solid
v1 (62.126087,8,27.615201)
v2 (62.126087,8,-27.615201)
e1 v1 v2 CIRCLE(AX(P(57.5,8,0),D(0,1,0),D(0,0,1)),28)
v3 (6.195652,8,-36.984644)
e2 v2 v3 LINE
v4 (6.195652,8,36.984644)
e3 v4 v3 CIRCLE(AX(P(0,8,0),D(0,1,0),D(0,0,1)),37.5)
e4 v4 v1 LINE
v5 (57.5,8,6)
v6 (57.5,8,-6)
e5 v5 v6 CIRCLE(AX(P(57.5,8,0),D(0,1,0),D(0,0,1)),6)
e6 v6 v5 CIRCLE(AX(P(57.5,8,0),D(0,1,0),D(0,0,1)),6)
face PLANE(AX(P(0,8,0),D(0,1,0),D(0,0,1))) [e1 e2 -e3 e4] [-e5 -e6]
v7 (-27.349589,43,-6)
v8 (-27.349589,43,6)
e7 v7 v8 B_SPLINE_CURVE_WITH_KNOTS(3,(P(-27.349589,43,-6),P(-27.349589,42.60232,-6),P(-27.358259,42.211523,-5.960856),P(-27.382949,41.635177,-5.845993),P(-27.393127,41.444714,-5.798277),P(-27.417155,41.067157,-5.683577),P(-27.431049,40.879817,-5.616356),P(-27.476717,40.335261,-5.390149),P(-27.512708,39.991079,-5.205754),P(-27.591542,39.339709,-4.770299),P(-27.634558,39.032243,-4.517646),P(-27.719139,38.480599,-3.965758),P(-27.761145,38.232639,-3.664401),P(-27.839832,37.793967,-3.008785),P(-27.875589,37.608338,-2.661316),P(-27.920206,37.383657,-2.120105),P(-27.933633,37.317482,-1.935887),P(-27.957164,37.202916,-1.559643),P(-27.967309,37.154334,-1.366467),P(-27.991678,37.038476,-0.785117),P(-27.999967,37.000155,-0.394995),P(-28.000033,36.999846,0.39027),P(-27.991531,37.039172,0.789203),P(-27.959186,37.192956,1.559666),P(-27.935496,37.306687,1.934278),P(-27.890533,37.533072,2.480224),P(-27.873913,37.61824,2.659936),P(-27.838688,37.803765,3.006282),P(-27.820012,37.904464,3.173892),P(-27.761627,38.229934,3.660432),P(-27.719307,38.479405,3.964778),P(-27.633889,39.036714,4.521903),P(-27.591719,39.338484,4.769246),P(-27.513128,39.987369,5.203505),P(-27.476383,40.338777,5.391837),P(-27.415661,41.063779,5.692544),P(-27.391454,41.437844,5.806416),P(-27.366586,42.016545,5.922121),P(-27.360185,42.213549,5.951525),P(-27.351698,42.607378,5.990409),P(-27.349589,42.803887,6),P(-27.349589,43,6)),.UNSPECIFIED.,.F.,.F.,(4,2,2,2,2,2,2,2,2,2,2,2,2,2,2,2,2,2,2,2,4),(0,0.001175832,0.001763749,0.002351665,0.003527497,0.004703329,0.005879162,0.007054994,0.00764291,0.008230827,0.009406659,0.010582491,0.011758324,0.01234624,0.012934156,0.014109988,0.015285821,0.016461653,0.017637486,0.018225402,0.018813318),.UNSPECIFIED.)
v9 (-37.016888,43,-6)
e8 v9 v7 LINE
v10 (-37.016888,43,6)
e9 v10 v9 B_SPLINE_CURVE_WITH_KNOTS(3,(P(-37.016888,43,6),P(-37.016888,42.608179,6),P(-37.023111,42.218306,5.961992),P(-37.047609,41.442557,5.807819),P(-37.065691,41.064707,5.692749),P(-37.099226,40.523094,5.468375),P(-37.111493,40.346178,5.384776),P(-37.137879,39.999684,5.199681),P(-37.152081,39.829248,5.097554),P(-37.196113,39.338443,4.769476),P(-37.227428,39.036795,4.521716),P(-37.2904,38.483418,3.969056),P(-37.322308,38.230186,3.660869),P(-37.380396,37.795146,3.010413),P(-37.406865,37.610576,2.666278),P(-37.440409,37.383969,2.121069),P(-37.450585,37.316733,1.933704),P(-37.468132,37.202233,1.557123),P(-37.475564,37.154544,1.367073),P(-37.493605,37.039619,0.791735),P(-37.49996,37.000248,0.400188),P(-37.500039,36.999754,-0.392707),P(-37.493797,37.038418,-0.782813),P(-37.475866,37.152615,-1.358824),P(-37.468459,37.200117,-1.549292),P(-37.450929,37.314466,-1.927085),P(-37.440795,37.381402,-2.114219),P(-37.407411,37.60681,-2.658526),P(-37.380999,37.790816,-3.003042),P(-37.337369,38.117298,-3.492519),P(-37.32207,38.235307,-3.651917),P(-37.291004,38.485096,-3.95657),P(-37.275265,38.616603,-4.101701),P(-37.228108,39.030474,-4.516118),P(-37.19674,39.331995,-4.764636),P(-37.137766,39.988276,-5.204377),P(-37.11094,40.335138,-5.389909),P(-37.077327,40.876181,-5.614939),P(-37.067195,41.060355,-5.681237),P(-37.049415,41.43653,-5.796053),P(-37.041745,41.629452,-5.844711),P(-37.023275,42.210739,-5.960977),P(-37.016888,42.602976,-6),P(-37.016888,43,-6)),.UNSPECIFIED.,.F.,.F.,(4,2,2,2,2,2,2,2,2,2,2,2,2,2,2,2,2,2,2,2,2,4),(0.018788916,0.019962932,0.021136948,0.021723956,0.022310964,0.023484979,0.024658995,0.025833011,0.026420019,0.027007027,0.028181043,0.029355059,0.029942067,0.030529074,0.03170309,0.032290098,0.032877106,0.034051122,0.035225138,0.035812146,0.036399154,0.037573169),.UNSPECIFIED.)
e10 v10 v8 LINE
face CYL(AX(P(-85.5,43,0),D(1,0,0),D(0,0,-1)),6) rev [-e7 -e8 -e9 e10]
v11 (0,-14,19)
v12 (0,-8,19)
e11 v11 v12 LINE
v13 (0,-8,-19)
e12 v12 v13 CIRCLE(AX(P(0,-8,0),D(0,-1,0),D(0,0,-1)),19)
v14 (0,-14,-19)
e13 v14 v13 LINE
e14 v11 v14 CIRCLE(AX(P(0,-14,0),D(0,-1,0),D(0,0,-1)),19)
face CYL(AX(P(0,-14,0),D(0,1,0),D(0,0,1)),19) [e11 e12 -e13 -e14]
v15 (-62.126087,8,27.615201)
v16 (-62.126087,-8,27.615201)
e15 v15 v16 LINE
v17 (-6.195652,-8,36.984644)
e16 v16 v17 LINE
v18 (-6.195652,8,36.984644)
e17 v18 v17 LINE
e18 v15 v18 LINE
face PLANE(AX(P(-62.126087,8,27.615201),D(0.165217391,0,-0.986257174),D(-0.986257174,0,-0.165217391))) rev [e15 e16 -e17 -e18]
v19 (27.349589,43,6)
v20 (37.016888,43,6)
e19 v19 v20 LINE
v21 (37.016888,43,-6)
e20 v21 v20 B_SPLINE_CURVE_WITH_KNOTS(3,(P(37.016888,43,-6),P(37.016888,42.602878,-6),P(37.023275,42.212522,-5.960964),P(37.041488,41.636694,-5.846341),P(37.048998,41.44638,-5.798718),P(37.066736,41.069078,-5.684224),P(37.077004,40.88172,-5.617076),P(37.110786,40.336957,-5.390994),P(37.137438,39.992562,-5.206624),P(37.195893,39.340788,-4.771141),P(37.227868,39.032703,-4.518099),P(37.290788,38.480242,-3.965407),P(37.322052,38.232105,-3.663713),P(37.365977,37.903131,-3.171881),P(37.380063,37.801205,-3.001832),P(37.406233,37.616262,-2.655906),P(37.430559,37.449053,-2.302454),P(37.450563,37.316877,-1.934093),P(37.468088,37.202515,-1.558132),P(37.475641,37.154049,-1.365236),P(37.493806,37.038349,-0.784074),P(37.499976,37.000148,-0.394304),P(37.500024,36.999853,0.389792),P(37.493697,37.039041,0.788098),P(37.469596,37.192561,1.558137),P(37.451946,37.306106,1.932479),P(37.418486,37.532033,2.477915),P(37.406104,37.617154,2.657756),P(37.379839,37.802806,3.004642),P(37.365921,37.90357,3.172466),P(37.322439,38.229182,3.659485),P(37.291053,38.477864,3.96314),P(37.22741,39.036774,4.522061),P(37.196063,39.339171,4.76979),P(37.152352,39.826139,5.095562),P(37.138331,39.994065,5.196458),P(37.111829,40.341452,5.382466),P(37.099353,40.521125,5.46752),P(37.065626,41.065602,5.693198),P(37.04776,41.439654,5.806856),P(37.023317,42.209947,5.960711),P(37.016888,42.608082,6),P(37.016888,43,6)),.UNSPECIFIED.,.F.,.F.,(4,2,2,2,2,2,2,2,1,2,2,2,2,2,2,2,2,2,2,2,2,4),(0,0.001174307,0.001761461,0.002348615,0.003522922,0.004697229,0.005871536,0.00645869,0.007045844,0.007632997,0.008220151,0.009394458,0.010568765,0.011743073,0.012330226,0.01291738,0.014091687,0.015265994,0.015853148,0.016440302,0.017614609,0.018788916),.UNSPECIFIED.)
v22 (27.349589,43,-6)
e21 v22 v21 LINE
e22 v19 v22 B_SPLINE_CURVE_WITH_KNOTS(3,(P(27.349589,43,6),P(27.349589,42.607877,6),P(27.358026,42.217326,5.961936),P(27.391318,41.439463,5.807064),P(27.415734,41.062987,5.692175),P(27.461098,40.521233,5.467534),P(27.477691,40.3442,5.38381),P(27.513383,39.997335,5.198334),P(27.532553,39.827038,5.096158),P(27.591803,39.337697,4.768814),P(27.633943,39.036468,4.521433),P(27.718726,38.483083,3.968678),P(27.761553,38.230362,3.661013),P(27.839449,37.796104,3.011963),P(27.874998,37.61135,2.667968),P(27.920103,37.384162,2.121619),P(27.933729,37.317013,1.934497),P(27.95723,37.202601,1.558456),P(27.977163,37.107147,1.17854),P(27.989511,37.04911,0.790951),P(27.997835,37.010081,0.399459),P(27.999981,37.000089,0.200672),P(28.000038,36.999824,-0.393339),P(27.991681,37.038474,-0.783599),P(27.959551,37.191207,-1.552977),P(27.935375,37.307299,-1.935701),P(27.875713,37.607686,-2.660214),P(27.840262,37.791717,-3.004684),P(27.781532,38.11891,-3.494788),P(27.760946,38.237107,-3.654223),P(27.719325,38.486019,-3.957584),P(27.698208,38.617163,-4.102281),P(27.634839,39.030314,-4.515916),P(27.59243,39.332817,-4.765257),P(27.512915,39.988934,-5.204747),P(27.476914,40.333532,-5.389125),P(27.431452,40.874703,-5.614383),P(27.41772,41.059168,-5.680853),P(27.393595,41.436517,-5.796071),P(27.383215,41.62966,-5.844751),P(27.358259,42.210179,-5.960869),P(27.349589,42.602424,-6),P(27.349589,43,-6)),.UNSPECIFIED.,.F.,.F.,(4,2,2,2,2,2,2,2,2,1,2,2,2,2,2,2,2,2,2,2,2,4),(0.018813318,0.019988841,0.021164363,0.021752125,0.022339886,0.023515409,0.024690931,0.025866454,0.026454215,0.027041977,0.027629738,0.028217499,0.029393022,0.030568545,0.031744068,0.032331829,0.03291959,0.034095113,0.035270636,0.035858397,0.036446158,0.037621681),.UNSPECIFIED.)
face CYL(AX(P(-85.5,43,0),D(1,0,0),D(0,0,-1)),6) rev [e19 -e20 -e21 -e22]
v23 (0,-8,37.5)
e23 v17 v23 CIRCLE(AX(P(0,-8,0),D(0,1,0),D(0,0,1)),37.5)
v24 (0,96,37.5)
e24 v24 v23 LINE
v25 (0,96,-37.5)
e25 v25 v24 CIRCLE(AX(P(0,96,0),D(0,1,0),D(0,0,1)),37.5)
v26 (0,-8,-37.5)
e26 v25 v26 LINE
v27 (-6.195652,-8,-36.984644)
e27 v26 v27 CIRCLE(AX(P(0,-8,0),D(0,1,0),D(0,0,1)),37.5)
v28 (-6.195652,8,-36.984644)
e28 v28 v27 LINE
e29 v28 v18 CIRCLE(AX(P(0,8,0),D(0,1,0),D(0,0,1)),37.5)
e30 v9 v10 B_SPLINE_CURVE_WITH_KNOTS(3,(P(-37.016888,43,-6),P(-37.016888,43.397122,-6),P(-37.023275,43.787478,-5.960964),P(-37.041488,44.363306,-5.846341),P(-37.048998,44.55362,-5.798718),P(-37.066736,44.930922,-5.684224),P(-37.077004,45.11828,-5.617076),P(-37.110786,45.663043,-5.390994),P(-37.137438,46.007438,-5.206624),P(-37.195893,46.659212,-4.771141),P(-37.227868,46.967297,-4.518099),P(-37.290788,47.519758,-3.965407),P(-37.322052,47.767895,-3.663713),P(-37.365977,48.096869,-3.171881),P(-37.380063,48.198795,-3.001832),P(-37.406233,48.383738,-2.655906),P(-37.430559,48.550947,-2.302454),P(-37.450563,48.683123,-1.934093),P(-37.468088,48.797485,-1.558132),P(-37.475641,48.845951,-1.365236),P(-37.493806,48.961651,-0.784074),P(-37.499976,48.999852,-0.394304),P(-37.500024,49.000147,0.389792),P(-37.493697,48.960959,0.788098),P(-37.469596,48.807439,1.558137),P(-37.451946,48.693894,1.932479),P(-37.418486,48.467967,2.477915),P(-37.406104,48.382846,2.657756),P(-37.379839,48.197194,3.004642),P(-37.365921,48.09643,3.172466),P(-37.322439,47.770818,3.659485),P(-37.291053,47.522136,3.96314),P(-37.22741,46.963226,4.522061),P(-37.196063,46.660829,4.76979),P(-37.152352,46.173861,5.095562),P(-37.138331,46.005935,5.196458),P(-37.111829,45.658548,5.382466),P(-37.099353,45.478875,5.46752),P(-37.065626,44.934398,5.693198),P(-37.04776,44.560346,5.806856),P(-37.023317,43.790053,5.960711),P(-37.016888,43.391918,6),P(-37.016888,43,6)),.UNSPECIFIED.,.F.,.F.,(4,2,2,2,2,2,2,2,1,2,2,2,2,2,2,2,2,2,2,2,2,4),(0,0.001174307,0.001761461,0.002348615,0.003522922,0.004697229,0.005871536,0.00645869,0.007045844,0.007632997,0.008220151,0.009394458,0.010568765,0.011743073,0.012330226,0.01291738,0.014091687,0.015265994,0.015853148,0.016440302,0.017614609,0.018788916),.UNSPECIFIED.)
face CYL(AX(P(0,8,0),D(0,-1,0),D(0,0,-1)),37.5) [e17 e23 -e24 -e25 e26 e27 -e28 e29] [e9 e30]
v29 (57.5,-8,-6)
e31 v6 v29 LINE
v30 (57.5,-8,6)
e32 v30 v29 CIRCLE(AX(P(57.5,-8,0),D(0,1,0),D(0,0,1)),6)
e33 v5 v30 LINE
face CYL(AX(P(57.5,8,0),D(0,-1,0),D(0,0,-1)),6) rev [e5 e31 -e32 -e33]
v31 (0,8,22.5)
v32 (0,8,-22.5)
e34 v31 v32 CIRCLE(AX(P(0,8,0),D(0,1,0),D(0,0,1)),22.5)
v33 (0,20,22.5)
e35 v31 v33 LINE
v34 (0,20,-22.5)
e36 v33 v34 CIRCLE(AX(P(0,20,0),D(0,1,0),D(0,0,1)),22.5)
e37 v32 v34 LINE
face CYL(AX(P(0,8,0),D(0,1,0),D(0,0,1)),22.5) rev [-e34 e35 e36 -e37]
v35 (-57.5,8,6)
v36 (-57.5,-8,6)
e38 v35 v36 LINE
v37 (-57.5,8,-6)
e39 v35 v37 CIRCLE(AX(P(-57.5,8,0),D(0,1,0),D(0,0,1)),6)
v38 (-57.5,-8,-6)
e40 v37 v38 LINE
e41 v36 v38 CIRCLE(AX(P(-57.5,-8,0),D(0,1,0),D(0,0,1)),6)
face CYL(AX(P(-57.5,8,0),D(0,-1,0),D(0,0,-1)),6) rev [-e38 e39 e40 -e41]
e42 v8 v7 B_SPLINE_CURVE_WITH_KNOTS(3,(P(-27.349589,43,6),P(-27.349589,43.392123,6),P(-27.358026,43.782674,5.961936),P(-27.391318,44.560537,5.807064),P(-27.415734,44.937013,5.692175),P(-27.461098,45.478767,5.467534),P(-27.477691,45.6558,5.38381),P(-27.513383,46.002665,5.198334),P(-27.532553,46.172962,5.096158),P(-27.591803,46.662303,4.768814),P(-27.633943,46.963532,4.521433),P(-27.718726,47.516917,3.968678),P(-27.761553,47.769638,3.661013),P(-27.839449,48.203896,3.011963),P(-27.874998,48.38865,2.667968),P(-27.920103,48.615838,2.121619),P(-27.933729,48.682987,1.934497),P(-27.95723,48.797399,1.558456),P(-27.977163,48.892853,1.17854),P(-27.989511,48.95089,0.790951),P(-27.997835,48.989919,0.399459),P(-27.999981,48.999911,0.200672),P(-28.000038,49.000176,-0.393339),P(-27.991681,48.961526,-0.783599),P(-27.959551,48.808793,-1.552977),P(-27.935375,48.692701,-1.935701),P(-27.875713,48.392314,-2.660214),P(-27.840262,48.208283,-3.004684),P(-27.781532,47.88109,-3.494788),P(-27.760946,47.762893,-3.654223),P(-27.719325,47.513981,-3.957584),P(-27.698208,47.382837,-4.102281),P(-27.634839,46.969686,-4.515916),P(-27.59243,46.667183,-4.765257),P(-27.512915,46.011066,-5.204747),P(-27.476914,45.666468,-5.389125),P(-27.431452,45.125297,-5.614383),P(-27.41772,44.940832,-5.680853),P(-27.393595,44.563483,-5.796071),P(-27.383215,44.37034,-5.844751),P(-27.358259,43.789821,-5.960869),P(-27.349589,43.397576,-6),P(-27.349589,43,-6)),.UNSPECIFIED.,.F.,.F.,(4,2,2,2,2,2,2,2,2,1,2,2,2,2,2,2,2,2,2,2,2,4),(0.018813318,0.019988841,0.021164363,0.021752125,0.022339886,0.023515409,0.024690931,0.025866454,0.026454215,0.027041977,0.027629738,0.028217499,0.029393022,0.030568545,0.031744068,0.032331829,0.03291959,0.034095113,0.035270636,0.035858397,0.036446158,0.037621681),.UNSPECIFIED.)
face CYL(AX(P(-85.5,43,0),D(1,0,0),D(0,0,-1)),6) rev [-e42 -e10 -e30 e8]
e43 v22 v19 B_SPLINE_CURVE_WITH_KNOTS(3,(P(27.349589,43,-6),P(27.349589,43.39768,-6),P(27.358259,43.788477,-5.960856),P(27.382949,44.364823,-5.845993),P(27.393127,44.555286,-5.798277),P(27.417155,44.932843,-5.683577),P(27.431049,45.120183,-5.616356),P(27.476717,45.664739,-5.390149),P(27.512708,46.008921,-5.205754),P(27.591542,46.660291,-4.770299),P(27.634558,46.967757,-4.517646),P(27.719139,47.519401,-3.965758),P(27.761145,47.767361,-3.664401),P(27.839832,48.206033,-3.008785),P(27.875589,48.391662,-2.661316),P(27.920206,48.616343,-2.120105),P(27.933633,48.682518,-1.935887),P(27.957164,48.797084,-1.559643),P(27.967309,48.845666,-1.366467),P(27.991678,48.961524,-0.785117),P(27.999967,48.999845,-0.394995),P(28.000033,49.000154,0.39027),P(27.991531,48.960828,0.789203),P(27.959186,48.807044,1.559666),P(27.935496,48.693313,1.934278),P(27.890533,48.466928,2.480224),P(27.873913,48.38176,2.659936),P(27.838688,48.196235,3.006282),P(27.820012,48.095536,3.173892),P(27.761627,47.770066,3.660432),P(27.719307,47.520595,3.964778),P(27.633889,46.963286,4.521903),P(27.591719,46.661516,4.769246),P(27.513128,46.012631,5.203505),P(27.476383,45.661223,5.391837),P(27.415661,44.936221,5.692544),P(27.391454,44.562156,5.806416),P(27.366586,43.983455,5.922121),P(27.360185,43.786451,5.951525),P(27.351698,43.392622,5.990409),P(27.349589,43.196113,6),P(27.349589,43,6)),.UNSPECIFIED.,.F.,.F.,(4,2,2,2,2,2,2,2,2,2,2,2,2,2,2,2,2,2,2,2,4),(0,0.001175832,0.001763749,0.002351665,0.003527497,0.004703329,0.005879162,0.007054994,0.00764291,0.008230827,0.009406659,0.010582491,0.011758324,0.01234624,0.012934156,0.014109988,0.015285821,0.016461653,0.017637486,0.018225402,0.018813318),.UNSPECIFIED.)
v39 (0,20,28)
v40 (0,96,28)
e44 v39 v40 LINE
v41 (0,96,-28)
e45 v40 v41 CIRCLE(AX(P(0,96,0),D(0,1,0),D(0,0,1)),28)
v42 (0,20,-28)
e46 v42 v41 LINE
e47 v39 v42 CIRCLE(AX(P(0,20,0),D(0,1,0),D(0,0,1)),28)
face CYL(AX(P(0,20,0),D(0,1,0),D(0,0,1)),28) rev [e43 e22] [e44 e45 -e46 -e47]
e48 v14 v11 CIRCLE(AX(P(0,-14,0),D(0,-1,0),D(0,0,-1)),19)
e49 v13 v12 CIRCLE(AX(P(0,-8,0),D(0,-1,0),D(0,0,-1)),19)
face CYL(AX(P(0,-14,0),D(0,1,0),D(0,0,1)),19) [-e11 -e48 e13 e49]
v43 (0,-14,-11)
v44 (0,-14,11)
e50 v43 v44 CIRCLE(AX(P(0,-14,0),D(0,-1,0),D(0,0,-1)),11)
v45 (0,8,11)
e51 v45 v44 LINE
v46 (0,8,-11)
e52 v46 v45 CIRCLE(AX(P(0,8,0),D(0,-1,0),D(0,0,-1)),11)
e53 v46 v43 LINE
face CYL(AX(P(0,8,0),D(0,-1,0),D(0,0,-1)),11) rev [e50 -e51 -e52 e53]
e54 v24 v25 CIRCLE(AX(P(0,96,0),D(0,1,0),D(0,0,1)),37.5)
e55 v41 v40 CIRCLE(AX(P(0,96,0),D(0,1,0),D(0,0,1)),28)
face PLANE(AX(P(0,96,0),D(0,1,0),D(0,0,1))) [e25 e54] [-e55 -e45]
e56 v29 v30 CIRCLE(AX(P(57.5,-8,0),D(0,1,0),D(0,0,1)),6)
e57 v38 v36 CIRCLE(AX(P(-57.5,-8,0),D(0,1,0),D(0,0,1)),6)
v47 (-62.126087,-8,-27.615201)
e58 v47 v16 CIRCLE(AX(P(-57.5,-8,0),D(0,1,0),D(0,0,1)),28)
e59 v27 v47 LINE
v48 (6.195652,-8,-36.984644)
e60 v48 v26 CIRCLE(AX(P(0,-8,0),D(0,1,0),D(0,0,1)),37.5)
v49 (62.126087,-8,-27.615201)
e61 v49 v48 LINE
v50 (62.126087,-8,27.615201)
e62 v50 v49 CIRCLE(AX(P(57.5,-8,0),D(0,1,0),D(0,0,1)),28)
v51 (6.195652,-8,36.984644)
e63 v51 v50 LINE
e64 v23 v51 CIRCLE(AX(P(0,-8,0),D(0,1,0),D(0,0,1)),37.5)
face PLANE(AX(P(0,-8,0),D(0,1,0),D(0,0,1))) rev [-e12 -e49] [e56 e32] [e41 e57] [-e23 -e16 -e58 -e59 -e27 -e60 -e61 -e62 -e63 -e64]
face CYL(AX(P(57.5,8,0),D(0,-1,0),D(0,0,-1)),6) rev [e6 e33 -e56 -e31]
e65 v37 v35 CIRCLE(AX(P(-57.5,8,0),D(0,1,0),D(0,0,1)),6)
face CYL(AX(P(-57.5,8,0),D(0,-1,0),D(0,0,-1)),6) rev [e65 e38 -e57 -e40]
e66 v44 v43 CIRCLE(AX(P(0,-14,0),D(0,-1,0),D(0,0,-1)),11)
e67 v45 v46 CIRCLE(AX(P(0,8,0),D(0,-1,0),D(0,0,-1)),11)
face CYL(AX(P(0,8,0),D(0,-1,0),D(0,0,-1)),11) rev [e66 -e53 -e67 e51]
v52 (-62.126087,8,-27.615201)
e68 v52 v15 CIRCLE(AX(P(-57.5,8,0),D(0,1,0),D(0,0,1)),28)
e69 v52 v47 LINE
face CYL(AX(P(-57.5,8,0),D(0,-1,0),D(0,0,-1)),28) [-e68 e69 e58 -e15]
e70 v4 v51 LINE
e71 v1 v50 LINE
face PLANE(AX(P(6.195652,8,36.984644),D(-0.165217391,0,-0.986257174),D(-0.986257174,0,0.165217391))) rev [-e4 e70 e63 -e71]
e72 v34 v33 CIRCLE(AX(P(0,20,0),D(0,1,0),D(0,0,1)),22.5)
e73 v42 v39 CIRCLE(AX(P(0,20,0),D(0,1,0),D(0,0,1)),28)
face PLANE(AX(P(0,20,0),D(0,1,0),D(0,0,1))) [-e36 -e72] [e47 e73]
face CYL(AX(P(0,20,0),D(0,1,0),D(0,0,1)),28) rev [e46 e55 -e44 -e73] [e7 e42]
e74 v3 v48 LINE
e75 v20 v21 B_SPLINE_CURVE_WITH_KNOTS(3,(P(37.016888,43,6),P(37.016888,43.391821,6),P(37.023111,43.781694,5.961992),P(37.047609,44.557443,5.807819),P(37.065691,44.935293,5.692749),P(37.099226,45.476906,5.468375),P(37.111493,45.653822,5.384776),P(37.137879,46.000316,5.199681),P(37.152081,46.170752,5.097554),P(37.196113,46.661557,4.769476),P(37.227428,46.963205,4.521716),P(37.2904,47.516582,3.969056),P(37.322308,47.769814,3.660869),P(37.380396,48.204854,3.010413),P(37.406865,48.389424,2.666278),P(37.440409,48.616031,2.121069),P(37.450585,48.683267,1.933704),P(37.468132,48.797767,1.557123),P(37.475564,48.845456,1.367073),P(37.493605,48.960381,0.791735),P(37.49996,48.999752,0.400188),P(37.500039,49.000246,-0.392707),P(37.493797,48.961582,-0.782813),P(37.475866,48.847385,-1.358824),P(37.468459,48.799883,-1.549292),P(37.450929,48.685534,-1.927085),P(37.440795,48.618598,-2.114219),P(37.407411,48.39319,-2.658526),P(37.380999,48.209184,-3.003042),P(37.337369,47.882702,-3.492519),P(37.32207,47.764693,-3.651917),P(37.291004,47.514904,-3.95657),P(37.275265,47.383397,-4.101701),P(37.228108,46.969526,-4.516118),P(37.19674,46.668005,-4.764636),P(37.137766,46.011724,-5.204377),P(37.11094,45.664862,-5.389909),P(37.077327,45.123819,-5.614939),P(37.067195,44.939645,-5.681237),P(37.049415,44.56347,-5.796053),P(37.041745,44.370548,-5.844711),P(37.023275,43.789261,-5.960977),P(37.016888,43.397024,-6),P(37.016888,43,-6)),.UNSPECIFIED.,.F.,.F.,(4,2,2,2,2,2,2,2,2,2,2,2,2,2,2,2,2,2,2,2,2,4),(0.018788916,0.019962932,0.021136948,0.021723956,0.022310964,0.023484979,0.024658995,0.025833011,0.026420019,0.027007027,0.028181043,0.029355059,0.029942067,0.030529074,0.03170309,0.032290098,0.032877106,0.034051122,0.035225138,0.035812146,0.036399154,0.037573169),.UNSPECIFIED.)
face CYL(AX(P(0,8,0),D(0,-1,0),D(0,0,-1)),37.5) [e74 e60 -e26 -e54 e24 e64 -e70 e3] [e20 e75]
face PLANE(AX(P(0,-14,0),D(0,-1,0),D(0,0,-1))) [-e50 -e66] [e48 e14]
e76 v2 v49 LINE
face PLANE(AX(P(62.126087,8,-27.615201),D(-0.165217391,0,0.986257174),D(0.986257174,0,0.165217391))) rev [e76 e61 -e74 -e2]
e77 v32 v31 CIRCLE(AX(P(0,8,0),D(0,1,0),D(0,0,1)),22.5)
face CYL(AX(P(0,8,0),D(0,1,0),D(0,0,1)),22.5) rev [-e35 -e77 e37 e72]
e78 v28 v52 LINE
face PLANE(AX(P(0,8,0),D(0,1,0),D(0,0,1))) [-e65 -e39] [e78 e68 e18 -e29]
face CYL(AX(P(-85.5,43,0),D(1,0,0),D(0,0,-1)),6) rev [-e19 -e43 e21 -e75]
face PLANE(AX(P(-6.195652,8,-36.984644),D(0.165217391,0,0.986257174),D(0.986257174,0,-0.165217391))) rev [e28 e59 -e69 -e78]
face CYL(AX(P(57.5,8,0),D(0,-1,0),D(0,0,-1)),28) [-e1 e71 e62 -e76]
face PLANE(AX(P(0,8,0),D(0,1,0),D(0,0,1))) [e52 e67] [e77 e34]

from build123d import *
from build123d.topology import SkipClean

# Parameters (mm, degrees)
BASE_FLANGE_SKETCH_R     = 6
BASE_FLANGE_DEPTH        = 8
TUBE_START               = 88
TUBE_SKETCH_R            = 37.5
TUBE_75_DEPTH            = 88
BORE_SKETCH_R            = 28
BORE_56_DEPTH            = 76
SPIGOT_SKETCH_R          = 19
SPIGOT_38_DEPTH          = 6
SPIGOT_HOLE_SKETCH_R     = 11
SPIGOT_HOLE_22_DEPTH     = 22
BORE_STEP_SKETCH_R       = 22.5
BORE_STEP_45_DEPTH       = 12
CROSS_HOLE_12_DEPTH      = 134.912284724
CROSS_HOLE_12_DEPTH_BACK = 134.912284724
CROSS_HOLE_SKETCH_R      = 6


with BuildPart() as part:
    # Base Flange Sketch → Base Flange (new, symmetric)
    with BuildSketch(Plane(origin=(0, 0, 0), x_dir=(1, 0, 0), z_dir=(0, 1, 0))):
        with BuildLine():
            Line((-62.126086957, -27.615200877), (-6.195652174, -36.984644032))
            ThreePointArc((-6.195652174, -36.984644032), (0, -37.5), (6.195652174, -36.984644032))
            Line((6.195652174, -36.984644032), (62.126086957, -27.615200877))
            ThreePointArc((62.126086957, -27.615200877), (85.5, 0), (62.126086957, 27.615200877))
            Line((62.126086957, 27.615200877), (6.195652174, 36.984644032))
            ThreePointArc((6.195652174, 36.984644032), (0, 37.5), (-6.195652174, 36.984644032))
            Line((-6.195652174, 36.984644032), (-62.126086957, 27.615200877))
            ThreePointArc((-62.126086957, 27.615200877), (-85.5, 0), (-62.126086957, -27.615200877))
        make_face()
        with Locations(Location((-57.5, 0, 0), (0, 0, 270))):
            Circle(BASE_FLANGE_SKETCH_R, mode=Mode.SUBTRACT)
        with Locations(Location((57.5, 0, 0), (0, 0, 270))):
            Circle(BASE_FLANGE_SKETCH_R, mode=Mode.SUBTRACT)
    extrude(amount=BASE_FLANGE_DEPTH, both=True)

    # Tube Sketch → Tube Ø75 (add)
    with SkipClean():  # the faces are left unmerged after this step: merging them gives an invalid solid
        with BuildSketch(Plane(origin=(0, 8, 0), x_dir=(1, 0, 0), z_dir=(0, 1, 0)).offset(TUBE_START)):
            with Locations(Location((0, 0, 0), (0, 0, 99.5098634))):
                Circle(TUBE_SKETCH_R)
        extrude(amount=-TUBE_75_DEPTH)

    # Bore Sketch → Bore Ø56 (cut)
    with SkipClean():  # the faces are left unmerged after this step: merging them gives an invalid solid
        with BuildSketch(Plane(origin=(0, 96, 0), x_dir=(1, 0, 0), z_dir=(0, 1, 0))):
            with Locations(Location((0, 0, 0), (0, 0, 270))):
                Circle(BORE_SKETCH_R)
        extrude(amount=-BORE_56_DEPTH, mode=Mode.SUBTRACT)

    # Spigot Sketch → Spigot Ø38 (add)
    with SkipClean():  # the faces are left unmerged after this step: merging them gives an invalid solid
        with BuildSketch(Plane.XZ.offset(8)):
            with Locations(Location((0, 0, 0), (0, 0, 270))):
                Circle(SPIGOT_SKETCH_R)
        extrude(amount=SPIGOT_38_DEPTH)

    # Spigot Hole Sketch → Spigot Hole Ø22 (cut)
    with SkipClean():  # the faces are left unmerged after this step: merging them gives an invalid solid
        with BuildSketch(Plane.XZ.offset(14)):
            with Locations(Location((0, 0, 0), (0, 0, 270))):
                Circle(SPIGOT_HOLE_SKETCH_R)
        extrude(amount=-SPIGOT_HOLE_22_DEPTH, mode=Mode.SUBTRACT)

    # Bore Step Sketch → Bore Step Ø45 (cut)
    with SkipClean():  # the faces are left unmerged after this step: merging them gives an invalid solid
        with BuildSketch(Plane(origin=(0, 20, 0), x_dir=(1, 0, 0), z_dir=(0, 1, 0))):
            with Locations(Location((0, 0, 0), (0, 0, 270))):
                Circle(BORE_STEP_SKETCH_R)
        extrude(amount=-BORE_STEP_45_DEPTH, mode=Mode.SUBTRACT)

    # Cross Hole Sketch → Cross Hole Ø12 (cut, two sides: drawn at the far end of the back side and taken through both)
    with SkipClean():  # the faces are left unmerged after this step: merging them gives an invalid solid
        with BuildSketch(Plane(origin=(0, 0, 0), x_dir=(0, 0, -1), z_dir=(1, 0, 0)).offset(-CROSS_HOLE_12_DEPTH_BACK)):
            with Locations((0, 43)):
                Circle(CROSS_HOLE_SKETCH_R)
        extrude(amount=CROSS_HOLE_12_DEPTH + CROSS_HOLE_12_DEPTH_BACK, mode=Mode.SUBTRACT)


solid = part.part
